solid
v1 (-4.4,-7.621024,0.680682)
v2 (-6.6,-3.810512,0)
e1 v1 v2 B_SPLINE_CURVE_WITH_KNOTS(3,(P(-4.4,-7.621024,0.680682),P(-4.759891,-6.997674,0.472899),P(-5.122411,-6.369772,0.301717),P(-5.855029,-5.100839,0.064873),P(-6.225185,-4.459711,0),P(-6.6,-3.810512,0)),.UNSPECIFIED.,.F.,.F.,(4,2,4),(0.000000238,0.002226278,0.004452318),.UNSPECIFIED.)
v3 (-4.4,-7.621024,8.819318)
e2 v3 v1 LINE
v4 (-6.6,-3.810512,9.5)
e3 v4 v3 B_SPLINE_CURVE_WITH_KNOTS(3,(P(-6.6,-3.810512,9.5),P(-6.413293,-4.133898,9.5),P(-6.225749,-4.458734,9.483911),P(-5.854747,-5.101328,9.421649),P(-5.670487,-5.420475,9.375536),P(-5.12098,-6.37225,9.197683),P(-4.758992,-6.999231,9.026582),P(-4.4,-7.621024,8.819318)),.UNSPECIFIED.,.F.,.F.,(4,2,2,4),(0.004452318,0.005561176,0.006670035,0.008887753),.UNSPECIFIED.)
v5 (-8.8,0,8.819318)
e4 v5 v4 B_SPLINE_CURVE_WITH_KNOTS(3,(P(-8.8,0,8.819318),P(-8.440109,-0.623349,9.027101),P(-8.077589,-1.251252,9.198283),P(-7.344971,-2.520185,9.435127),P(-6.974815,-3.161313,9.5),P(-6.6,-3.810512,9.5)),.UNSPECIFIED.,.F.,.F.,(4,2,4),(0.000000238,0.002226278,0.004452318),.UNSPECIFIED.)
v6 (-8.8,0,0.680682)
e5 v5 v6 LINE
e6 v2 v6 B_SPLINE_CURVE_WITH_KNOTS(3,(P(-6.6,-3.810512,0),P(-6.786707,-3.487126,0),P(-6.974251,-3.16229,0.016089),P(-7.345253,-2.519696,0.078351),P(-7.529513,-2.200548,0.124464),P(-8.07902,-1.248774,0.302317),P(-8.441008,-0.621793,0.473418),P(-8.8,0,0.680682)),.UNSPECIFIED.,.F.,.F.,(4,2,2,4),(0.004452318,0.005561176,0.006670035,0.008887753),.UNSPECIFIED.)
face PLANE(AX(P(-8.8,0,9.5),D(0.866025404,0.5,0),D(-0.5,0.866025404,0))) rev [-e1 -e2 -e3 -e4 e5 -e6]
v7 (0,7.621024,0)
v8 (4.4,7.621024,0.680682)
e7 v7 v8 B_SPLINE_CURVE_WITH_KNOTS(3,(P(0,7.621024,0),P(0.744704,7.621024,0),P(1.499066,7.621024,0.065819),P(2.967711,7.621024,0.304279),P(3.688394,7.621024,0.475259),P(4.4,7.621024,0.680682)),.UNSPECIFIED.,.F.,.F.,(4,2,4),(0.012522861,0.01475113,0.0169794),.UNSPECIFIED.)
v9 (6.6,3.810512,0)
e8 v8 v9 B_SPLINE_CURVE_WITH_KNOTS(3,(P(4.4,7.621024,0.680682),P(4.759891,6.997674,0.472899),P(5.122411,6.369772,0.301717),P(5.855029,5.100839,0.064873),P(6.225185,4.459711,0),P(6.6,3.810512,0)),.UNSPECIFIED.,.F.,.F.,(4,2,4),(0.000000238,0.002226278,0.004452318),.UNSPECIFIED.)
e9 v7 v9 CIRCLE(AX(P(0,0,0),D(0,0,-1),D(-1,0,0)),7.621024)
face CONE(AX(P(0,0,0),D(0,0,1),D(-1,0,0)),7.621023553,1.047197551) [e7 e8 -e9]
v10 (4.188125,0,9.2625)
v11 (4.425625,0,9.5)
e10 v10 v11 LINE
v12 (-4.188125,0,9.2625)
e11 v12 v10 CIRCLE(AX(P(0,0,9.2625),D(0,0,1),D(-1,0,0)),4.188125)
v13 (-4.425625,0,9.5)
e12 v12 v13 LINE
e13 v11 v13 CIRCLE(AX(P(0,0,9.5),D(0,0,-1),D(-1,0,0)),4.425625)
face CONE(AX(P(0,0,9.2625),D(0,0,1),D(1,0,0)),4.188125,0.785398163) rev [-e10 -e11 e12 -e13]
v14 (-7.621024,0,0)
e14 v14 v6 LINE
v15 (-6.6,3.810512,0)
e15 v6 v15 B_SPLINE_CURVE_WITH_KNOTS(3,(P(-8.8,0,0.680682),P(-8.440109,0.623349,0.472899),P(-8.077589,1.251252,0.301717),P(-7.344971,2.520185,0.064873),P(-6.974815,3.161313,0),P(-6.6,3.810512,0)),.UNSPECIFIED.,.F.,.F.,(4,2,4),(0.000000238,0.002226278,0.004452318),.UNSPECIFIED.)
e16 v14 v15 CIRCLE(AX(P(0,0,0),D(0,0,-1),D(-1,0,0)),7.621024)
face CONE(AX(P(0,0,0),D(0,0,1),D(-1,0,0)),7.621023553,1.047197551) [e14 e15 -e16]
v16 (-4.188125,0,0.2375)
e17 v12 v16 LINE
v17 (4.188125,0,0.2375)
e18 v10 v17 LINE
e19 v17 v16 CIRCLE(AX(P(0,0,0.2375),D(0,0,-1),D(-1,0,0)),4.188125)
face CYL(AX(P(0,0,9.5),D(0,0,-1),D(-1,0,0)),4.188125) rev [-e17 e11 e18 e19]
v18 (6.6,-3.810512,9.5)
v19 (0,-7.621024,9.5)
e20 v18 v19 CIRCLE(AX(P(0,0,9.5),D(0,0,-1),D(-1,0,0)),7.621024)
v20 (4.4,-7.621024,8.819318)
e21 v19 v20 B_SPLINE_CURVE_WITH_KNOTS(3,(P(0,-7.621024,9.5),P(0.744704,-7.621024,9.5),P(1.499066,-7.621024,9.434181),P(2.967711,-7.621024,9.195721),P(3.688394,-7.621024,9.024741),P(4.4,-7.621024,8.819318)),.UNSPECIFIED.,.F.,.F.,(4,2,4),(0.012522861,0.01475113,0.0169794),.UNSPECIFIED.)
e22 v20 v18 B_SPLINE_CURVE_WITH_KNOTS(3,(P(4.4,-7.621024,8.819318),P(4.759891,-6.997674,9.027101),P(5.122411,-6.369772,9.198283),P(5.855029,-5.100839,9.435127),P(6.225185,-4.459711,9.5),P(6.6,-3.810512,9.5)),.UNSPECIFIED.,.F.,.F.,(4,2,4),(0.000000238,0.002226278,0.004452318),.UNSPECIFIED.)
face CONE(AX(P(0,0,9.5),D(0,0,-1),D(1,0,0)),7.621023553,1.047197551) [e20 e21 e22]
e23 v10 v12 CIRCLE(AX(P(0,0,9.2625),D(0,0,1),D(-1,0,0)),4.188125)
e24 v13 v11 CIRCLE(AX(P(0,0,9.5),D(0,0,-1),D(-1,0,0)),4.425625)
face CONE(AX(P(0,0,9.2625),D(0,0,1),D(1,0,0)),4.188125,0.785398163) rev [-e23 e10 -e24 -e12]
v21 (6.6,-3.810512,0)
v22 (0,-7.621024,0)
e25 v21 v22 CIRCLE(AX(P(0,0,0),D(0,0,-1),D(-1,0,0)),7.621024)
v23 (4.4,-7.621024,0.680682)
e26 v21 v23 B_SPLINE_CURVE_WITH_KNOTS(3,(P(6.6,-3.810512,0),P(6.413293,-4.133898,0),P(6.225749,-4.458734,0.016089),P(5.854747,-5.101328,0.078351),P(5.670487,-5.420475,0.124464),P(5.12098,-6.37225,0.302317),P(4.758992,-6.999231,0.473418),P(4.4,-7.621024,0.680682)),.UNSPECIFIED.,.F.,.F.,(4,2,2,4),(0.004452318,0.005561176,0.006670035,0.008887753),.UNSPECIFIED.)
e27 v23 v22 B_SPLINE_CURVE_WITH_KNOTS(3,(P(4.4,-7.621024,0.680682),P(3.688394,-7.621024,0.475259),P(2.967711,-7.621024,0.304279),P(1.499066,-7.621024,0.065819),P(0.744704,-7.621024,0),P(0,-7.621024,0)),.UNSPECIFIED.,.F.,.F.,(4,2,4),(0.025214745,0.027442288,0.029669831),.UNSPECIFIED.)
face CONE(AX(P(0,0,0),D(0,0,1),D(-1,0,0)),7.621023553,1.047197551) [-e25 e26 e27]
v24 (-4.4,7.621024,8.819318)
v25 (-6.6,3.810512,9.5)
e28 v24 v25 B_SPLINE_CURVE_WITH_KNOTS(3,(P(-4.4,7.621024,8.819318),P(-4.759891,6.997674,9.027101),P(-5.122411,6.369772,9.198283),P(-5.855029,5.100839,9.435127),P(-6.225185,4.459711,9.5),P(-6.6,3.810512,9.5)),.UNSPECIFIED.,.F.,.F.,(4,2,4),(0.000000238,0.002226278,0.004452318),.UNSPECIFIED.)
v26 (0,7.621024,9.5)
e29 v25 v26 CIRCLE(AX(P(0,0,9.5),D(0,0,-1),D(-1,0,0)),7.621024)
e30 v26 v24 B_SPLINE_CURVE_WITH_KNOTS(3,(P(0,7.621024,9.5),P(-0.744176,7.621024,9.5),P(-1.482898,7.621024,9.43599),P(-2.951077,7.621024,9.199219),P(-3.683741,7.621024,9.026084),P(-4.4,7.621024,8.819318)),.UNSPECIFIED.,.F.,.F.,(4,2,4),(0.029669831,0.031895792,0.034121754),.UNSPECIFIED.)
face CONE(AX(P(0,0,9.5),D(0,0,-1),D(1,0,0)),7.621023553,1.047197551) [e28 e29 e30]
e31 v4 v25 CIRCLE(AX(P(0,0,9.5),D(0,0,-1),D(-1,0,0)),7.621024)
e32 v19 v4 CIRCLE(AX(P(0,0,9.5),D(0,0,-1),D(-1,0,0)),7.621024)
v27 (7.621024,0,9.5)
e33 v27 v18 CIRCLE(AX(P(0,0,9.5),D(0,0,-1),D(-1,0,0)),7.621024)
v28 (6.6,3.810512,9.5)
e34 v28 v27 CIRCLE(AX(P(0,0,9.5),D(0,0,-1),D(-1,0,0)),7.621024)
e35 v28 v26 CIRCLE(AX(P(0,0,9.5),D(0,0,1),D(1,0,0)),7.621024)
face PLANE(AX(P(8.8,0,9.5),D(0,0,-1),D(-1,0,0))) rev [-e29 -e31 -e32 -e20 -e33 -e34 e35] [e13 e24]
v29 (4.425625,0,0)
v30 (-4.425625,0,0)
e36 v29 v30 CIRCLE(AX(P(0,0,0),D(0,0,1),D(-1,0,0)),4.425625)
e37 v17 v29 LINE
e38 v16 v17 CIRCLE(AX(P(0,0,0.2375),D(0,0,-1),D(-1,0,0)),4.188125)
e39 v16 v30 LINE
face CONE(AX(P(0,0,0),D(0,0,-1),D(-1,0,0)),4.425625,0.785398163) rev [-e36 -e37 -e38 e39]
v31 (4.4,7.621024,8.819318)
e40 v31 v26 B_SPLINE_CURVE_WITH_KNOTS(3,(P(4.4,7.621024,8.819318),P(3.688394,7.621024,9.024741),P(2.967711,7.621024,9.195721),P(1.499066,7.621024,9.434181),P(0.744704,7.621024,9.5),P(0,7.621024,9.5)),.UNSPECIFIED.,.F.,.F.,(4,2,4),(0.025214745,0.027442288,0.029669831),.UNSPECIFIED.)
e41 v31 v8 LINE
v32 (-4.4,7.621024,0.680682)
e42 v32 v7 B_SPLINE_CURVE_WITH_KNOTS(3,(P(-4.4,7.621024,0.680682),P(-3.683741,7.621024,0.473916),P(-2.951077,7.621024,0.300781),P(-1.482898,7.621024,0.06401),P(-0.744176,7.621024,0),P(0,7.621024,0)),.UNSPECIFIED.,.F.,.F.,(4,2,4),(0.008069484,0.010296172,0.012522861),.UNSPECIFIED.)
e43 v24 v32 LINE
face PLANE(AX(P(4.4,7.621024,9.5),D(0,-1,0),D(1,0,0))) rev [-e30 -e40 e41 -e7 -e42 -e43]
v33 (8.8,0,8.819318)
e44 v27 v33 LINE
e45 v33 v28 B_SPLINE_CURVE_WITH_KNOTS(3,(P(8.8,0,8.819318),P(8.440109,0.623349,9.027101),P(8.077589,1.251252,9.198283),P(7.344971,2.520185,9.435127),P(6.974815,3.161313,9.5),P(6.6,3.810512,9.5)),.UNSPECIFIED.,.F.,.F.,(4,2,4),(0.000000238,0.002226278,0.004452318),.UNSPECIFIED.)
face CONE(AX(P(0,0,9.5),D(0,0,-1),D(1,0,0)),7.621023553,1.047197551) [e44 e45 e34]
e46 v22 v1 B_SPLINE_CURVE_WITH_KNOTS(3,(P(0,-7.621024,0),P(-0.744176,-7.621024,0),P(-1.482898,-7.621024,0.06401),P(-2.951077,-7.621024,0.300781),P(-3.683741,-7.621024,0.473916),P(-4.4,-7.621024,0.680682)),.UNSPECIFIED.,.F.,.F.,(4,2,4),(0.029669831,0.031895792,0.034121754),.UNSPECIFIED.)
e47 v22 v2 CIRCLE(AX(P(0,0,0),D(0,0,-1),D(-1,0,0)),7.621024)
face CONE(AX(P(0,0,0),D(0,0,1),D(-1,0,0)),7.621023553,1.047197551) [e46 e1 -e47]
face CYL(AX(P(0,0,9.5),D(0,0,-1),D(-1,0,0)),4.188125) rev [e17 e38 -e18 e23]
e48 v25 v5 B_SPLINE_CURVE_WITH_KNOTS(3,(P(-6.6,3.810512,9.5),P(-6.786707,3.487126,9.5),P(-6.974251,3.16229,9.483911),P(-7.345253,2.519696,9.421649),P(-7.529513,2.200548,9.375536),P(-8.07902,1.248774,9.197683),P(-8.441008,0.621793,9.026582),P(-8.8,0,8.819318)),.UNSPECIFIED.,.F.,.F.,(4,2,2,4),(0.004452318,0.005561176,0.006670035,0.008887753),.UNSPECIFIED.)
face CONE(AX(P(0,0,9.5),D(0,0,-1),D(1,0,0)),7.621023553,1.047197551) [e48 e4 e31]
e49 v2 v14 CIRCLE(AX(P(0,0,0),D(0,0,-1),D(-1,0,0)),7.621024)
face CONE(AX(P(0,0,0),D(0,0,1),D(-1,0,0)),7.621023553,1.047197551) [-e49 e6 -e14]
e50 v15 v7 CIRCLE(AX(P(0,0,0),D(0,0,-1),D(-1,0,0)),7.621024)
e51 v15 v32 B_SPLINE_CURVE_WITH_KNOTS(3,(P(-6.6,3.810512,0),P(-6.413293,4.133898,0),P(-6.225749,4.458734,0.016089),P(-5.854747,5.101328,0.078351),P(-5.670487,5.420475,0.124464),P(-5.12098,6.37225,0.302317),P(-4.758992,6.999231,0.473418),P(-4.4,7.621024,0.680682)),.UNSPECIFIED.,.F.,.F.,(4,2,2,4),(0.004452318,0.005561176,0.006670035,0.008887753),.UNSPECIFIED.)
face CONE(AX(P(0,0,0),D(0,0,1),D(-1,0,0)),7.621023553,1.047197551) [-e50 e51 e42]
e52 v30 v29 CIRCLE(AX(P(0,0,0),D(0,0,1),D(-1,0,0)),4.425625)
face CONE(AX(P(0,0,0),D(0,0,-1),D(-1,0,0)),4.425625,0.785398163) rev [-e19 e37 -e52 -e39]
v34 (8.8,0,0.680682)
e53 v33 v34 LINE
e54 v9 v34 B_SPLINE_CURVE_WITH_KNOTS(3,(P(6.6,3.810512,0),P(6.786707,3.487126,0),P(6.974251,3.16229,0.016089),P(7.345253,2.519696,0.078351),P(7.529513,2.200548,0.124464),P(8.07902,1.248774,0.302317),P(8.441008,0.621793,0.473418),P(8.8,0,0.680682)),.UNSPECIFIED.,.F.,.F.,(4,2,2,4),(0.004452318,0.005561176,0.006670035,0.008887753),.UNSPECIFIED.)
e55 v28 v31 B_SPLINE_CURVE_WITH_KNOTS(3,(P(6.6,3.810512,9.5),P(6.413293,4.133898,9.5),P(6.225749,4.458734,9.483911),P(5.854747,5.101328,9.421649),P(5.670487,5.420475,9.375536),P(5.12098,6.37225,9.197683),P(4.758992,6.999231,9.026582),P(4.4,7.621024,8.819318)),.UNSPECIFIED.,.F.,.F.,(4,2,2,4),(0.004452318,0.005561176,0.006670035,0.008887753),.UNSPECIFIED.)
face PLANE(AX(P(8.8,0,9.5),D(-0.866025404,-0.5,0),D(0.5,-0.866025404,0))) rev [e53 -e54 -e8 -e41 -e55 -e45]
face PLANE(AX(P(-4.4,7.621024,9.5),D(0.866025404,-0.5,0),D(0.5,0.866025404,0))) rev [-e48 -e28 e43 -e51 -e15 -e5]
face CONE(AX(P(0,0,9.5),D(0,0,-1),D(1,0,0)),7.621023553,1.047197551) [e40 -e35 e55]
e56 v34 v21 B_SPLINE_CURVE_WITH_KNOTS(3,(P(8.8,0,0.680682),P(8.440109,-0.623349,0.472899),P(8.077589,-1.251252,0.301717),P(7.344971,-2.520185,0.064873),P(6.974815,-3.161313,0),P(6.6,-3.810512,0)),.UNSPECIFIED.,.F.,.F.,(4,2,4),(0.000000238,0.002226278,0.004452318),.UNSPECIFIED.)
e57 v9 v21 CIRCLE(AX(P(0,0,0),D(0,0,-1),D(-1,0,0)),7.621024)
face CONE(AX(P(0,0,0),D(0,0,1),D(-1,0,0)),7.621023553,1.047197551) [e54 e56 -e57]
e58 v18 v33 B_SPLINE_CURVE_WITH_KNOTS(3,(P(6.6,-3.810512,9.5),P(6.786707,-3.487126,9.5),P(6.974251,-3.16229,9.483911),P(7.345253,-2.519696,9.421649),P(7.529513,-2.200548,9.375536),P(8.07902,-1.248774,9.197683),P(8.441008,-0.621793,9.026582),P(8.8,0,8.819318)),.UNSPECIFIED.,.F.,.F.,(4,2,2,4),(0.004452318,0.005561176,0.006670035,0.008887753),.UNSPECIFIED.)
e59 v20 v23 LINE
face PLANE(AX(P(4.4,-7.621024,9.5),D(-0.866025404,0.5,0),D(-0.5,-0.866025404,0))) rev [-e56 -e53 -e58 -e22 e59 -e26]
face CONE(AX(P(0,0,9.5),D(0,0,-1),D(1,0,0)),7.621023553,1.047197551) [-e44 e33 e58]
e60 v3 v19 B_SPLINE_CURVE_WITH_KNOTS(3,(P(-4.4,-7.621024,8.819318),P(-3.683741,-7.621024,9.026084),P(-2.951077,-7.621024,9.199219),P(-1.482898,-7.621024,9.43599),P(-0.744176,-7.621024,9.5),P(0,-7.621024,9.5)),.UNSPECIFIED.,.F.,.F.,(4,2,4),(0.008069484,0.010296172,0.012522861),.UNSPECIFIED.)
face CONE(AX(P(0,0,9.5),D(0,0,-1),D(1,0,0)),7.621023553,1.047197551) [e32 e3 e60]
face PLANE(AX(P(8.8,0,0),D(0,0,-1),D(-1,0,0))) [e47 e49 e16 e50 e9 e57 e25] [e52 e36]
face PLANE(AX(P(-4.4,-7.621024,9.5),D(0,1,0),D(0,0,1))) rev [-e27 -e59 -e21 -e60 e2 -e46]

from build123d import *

# Parameters (mm, degrees)
SKETCH1_R          = 4.188125
BOSS_EXTRUDE_DEPTH = 9.5
SKETCH2_OUTSIDE_W  = 80.144
SKETCH2_OUTSIDE_H  = 77.786
SKETCH2_OUTSIDE_R  = 7.621023553
CUT_EXTRUDE1_DEPTH = 16.025644745
CUT_EXTRUDE1_DRAFT = -60
SKETCH3_OUTSIDE_W  = 80.144
SKETCH3_OUTSIDE_H  = 77.786
SKETCH3_OUTSIDE_R  = 7.621023553
CUT_EXTRUDE2_DEPTH = 16.025644745
CUT_EXTRUDE2_DRAFT = -60
CHAMFER1_SIZE      = 0.2375


with BuildPart() as part:
    # Sketch1 → Boss-Extrude (new body)
    with BuildSketch(Plane.XY):
        Polygon((4.4, 7.621023553), (-4.4, 7.621023553), (-8.8, 0), (-4.4, -7.621023553), (4.4, -7.621023553), (8.8, 0), align=None)
        Circle(SKETCH1_R, mode=Mode.SUBTRACT)
    extrude(amount=BOSS_EXTRUDE_DEPTH)


with BuildPart() as cut_extrude1_tool:
    # Sketch2 outside → Cut-Extrude1 (with draft: the straight prism first)
    with BuildSketch(Plane(origin=(0, 0, 0), x_dir=(-1, 0, 0), z_dir=(0, 0, -1))):
        Rectangle(SKETCH2_OUTSIDE_W, SKETCH2_OUTSIDE_H)
        Circle(SKETCH2_OUTSIDE_R, mode=Mode.SUBTRACT)
    extrude(amount=-CUT_EXTRUDE1_DEPTH)
    # Cut-Extrude1: the draft: its side faces are tilted about the plane it starts from
    cut_extrude1_sides = [cut_extrude1_tool.faces().sort_by_distance(p)[0] for p in [
        (0, -38.893, 8.012822372),
        (-40.072, 0, 8.012822372),
        (0, 38.893, 8.012822372),
        (40.072, 0, 8.012822372),
        (7.621023553, 0, 8.012822372),
    ]]
    draft(cut_extrude1_sides, Plane(origin=(0, 0, 0), x_dir=(-1, 0, 0), z_dir=(0, 0, -1)), CUT_EXTRUDE1_DRAFT)


with BuildPart() as part_1:
    add(part.part)

    # Cut-Extrude1: cut by cut_extrude1_tool
    add(cut_extrude1_tool.part, mode=Mode.SUBTRACT)


with BuildPart() as cut_extrude2_tool:
    # Sketch3 outside → Cut-Extrude2 (with draft: the straight prism first)
    with BuildSketch(Plane.XY.offset(9.5)):
        Rectangle(SKETCH3_OUTSIDE_W, SKETCH3_OUTSIDE_H)
        Circle(SKETCH3_OUTSIDE_R, mode=Mode.SUBTRACT)
    extrude(amount=-CUT_EXTRUDE2_DEPTH)
    # Cut-Extrude2: the draft: its side faces are tilted about the plane it starts from
    cut_extrude2_sides = [cut_extrude2_tool.faces().sort_by_distance(p)[0] for p in [
        (0, -38.893, 1.487177628),
        (40.072, 0, 1.487177628),
        (0, 38.893, 1.487177628),
        (-40.072, 0, 1.487177628),
        (-7.621023553, 0, 1.487177628),
    ]]
    draft(cut_extrude2_sides, Plane.XY.offset(9.5), CUT_EXTRUDE2_DRAFT)


with BuildPart() as part_2:
    add(part_1.part)

    # Cut-Extrude2: cut by cut_extrude2_tool
    add(cut_extrude2_tool.part, mode=Mode.SUBTRACT)

    # Chamfer1
    chamfer1_edges = [part_2.edges().sort_by_distance(p)[0] for p in [
        (-4.188125, 0, 0),
        (-4.188125, 0, 9.5),
    ]]
    chamfer(chamfer1_edges, length=CHAMFER1_SIZE)


solid = part_2.part
